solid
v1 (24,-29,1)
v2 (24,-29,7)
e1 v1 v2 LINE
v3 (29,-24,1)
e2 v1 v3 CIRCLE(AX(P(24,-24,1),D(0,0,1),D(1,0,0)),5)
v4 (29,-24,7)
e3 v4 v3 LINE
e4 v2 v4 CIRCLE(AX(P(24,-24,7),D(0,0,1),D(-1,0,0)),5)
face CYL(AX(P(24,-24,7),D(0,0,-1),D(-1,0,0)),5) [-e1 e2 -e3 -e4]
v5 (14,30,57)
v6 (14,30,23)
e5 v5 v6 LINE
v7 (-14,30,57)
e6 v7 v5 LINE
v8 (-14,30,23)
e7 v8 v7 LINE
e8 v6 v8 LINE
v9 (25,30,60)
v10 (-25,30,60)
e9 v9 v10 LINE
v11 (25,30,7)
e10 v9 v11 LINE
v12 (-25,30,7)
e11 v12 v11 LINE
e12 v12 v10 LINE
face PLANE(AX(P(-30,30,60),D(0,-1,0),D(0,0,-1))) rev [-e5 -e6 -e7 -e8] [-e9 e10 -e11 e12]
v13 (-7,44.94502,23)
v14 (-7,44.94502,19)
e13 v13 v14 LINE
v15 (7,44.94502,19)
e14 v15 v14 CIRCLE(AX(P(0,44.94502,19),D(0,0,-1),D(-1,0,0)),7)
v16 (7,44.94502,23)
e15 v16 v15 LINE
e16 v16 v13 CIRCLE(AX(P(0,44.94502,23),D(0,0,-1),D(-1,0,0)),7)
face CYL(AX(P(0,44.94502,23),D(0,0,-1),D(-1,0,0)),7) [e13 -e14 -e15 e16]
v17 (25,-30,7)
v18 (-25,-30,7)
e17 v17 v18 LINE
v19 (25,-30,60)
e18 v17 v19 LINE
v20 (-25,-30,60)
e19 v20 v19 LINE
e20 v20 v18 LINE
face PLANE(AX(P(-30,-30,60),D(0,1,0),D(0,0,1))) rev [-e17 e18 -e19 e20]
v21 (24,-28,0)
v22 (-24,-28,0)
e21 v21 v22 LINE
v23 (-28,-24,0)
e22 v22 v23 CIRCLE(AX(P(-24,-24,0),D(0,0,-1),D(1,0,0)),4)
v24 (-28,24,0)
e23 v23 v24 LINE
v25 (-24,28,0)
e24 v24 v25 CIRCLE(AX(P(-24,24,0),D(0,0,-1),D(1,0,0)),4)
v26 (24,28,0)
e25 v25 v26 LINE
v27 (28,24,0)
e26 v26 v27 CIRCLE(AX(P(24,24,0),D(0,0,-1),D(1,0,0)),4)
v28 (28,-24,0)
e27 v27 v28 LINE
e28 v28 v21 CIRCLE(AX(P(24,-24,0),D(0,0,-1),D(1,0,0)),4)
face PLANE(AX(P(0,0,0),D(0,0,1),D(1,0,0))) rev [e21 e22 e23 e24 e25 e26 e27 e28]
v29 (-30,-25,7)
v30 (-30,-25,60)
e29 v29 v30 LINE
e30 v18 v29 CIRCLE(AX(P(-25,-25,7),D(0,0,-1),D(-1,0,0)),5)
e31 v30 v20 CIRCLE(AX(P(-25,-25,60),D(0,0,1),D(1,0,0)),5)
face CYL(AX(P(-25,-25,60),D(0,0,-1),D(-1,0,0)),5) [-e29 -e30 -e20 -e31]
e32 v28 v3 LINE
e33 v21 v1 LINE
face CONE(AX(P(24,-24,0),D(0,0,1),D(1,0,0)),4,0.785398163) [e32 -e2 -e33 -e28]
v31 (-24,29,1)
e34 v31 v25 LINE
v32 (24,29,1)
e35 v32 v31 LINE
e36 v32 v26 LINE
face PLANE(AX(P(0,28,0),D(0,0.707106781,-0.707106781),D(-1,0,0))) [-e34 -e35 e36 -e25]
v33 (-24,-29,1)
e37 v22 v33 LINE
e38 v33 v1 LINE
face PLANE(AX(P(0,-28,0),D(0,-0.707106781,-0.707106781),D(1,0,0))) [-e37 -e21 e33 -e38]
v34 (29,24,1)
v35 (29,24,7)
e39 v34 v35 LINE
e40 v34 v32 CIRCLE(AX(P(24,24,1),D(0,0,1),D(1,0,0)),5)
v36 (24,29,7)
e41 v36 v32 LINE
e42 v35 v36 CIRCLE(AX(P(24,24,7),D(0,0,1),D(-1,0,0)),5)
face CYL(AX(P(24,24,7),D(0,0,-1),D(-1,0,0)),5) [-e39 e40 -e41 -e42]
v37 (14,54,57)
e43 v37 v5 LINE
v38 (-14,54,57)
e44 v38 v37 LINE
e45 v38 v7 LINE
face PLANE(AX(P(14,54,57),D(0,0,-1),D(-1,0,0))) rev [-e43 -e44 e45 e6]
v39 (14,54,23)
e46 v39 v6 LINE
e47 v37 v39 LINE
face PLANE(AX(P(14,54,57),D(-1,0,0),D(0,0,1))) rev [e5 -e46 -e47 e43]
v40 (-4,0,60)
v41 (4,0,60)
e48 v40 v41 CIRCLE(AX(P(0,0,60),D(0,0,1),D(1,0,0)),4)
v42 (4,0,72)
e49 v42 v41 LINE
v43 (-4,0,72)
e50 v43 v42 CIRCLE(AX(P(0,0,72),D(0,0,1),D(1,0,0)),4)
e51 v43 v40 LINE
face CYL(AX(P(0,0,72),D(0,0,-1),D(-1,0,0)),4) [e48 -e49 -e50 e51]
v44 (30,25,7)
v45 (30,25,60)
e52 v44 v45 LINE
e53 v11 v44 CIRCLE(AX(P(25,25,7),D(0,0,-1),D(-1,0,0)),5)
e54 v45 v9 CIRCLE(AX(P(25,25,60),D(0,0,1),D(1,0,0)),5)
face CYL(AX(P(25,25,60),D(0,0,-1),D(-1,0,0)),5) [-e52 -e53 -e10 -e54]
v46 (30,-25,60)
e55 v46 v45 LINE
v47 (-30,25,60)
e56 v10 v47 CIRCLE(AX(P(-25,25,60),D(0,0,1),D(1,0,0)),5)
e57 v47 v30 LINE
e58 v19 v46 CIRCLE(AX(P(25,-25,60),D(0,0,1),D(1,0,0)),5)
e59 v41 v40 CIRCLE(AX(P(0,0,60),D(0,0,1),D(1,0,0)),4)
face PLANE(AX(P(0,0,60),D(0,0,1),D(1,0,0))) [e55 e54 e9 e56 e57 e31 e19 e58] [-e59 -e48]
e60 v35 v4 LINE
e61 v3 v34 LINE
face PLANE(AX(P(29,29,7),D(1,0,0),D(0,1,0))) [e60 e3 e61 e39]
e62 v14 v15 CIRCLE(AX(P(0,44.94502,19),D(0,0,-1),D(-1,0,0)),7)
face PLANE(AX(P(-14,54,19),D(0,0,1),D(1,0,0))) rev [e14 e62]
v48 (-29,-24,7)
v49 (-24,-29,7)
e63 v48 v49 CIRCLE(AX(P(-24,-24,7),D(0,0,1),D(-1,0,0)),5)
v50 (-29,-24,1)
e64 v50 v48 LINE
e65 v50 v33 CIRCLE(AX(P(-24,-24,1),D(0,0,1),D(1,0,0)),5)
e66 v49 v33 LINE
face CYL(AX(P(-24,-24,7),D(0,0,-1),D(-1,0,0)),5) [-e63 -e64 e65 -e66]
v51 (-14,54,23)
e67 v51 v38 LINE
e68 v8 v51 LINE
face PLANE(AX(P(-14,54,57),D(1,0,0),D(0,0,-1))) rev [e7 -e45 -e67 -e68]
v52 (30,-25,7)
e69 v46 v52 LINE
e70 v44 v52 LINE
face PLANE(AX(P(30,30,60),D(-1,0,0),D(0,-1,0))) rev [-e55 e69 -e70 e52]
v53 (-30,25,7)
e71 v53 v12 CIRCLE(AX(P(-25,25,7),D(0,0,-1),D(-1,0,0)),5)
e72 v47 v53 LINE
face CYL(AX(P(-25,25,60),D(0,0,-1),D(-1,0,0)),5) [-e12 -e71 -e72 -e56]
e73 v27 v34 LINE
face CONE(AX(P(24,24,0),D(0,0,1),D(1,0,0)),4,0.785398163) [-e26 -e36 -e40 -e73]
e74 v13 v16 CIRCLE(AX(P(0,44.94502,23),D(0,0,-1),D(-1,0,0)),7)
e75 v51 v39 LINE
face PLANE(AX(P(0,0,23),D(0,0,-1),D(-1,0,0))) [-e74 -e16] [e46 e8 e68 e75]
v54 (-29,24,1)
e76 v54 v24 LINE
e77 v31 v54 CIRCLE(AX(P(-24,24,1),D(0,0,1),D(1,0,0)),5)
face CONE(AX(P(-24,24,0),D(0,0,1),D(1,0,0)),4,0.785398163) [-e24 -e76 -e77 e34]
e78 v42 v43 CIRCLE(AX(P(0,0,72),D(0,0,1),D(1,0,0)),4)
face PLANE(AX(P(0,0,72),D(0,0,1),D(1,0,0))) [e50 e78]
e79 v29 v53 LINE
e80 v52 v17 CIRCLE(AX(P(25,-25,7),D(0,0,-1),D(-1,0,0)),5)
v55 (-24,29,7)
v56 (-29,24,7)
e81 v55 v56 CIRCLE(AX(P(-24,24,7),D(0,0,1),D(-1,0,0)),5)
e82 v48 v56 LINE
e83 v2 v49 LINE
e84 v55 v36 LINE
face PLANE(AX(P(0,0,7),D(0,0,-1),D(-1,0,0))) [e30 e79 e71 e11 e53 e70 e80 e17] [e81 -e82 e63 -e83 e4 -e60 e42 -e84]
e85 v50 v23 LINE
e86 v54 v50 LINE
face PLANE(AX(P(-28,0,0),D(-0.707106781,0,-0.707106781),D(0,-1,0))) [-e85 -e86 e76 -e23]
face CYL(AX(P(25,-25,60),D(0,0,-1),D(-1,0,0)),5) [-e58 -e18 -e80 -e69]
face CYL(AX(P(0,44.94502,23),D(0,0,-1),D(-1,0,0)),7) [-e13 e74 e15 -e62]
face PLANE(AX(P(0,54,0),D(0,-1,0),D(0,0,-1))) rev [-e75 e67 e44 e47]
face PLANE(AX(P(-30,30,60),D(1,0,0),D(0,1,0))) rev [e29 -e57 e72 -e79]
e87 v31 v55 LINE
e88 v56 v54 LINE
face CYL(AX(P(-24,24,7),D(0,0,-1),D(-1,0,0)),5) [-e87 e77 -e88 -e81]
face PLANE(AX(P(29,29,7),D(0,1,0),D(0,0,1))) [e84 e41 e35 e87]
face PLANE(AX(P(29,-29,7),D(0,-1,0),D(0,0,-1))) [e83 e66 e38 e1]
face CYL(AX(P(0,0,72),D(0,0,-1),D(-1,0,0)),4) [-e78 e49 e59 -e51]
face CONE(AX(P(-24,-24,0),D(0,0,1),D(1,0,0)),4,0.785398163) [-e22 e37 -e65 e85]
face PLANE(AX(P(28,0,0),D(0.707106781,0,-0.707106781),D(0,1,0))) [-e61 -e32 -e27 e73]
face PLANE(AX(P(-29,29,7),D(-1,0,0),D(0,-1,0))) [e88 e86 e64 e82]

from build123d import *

# Parameters (mm, degrees)
SKETCH_1_W          = 60
SKETCH_1_H          = 60
EXTRUDE_1_DEPTH     = 60
SKETCH_3_R          = 4
EXTRUDE_2_DEPTH     = 12
SKETCH_4_W          = 60
SKETCH_4_H          = 60
SKETCH_4_W_2        = 58
SKETCH_4_H_2        = 58
CUT_EXTRUDE_4_DEPTH = 7
FILLET_4_R          = 5
CHAMFER_1_SIZE      = 1
FILLET_6_R          = 5
SKETCH_7_W          = 28
SKETCH_7_H          = 38
EXTRUDE_3_DEPTH     = 24
SKETCH_8_W          = 44.228024
SKETCH_8_H          = 29.89004
SKETCH_8_R          = 7
CUT_EXTRUDE_5_DEPTH = 4


with BuildPart() as part:
    # 草图1 → 凸台-拉伸1 (new body)
    with BuildSketch(Plane.XY):
        Rectangle(SKETCH_1_W, SKETCH_1_H)
    extrude(amount=EXTRUDE_1_DEPTH)

    # 草图3 → 凸台-拉伸2 (add)
    with BuildSketch(Plane.XY.offset(60)):
        Circle(SKETCH_3_R)
    extrude(amount=EXTRUDE_2_DEPTH)

    # 草图4 → 切除-拉伸4 (cut)
    with BuildSketch(Plane(origin=(0, 0, 0), x_dir=(-1, 0, 0), z_dir=(0, 0, -1))):
        Rectangle(SKETCH_4_W, SKETCH_4_H)
        Rectangle(SKETCH_4_W_2, SKETCH_4_H_2, mode=Mode.SUBTRACT)
    extrude(amount=-CUT_EXTRUDE_4_DEPTH, mode=Mode.SUBTRACT)

    # 圆角4
    fillet_4_edges = [part.edges().sort_by_distance(p)[0] for p in [
        (-29, -29, 3.5),
        (29, -29, 3.5),
        (29, 29, 3.5),
        (-29, 29, 3.5),
    ]]
    fillet(fillet_4_edges, radius=FILLET_4_R)

    # 倒角1
    chamfer_1_edges = [part.edges().sort_by_distance(p)[0] for p in [
        (0, 29, 0),
        (-29, 0, 0),
        (29, 0, 0),
        (0, -29, 0),
        (27.535533906, -27.535533906, 0),
        (-27.535533906, -27.535533906, 0),
        (-27.535533906, 27.535533906, 0),
        (27.535533906, 27.535533906, 0),
    ]]
    chamfer(chamfer_1_edges, length=CHAMFER_1_SIZE)

    # 圆角6
    fillet_6_edges = [part.edges().sort_by_distance(p)[0] for p in [
        (30, -30, 33.5),
        (-30, -30, 33.5),
        (-30, 30, 33.5),
        (30, 30, 33.5),
    ]]
    fillet(fillet_6_edges, radius=FILLET_6_R)

    # 草图7 → 凸台-拉伸3 (add)
    with BuildSketch(Plane(origin=(0, 30, 0), x_dir=(1, 0, 0), z_dir=(0, 1, 0))):
        with Locations((0, -38)):
            Rectangle(SKETCH_7_W, SKETCH_7_H)
    extrude(amount=EXTRUDE_3_DEPTH)

    # 草图8 → 切除-拉伸5 (cut)
    with BuildSketch(Plane(origin=(0, 0, 19), x_dir=(-1, 0, 0), z_dir=(0, 0, -1))):
        with Locations((0, 44.94502)):
            Rectangle(SKETCH_8_W, SKETCH_8_H)
        with Locations((0, 44.94502)):
            Circle(SKETCH_8_R, mode=Mode.SUBTRACT)
    extrude(amount=-CUT_EXTRUDE_5_DEPTH, mode=Mode.SUBTRACT)


solid = part.part
